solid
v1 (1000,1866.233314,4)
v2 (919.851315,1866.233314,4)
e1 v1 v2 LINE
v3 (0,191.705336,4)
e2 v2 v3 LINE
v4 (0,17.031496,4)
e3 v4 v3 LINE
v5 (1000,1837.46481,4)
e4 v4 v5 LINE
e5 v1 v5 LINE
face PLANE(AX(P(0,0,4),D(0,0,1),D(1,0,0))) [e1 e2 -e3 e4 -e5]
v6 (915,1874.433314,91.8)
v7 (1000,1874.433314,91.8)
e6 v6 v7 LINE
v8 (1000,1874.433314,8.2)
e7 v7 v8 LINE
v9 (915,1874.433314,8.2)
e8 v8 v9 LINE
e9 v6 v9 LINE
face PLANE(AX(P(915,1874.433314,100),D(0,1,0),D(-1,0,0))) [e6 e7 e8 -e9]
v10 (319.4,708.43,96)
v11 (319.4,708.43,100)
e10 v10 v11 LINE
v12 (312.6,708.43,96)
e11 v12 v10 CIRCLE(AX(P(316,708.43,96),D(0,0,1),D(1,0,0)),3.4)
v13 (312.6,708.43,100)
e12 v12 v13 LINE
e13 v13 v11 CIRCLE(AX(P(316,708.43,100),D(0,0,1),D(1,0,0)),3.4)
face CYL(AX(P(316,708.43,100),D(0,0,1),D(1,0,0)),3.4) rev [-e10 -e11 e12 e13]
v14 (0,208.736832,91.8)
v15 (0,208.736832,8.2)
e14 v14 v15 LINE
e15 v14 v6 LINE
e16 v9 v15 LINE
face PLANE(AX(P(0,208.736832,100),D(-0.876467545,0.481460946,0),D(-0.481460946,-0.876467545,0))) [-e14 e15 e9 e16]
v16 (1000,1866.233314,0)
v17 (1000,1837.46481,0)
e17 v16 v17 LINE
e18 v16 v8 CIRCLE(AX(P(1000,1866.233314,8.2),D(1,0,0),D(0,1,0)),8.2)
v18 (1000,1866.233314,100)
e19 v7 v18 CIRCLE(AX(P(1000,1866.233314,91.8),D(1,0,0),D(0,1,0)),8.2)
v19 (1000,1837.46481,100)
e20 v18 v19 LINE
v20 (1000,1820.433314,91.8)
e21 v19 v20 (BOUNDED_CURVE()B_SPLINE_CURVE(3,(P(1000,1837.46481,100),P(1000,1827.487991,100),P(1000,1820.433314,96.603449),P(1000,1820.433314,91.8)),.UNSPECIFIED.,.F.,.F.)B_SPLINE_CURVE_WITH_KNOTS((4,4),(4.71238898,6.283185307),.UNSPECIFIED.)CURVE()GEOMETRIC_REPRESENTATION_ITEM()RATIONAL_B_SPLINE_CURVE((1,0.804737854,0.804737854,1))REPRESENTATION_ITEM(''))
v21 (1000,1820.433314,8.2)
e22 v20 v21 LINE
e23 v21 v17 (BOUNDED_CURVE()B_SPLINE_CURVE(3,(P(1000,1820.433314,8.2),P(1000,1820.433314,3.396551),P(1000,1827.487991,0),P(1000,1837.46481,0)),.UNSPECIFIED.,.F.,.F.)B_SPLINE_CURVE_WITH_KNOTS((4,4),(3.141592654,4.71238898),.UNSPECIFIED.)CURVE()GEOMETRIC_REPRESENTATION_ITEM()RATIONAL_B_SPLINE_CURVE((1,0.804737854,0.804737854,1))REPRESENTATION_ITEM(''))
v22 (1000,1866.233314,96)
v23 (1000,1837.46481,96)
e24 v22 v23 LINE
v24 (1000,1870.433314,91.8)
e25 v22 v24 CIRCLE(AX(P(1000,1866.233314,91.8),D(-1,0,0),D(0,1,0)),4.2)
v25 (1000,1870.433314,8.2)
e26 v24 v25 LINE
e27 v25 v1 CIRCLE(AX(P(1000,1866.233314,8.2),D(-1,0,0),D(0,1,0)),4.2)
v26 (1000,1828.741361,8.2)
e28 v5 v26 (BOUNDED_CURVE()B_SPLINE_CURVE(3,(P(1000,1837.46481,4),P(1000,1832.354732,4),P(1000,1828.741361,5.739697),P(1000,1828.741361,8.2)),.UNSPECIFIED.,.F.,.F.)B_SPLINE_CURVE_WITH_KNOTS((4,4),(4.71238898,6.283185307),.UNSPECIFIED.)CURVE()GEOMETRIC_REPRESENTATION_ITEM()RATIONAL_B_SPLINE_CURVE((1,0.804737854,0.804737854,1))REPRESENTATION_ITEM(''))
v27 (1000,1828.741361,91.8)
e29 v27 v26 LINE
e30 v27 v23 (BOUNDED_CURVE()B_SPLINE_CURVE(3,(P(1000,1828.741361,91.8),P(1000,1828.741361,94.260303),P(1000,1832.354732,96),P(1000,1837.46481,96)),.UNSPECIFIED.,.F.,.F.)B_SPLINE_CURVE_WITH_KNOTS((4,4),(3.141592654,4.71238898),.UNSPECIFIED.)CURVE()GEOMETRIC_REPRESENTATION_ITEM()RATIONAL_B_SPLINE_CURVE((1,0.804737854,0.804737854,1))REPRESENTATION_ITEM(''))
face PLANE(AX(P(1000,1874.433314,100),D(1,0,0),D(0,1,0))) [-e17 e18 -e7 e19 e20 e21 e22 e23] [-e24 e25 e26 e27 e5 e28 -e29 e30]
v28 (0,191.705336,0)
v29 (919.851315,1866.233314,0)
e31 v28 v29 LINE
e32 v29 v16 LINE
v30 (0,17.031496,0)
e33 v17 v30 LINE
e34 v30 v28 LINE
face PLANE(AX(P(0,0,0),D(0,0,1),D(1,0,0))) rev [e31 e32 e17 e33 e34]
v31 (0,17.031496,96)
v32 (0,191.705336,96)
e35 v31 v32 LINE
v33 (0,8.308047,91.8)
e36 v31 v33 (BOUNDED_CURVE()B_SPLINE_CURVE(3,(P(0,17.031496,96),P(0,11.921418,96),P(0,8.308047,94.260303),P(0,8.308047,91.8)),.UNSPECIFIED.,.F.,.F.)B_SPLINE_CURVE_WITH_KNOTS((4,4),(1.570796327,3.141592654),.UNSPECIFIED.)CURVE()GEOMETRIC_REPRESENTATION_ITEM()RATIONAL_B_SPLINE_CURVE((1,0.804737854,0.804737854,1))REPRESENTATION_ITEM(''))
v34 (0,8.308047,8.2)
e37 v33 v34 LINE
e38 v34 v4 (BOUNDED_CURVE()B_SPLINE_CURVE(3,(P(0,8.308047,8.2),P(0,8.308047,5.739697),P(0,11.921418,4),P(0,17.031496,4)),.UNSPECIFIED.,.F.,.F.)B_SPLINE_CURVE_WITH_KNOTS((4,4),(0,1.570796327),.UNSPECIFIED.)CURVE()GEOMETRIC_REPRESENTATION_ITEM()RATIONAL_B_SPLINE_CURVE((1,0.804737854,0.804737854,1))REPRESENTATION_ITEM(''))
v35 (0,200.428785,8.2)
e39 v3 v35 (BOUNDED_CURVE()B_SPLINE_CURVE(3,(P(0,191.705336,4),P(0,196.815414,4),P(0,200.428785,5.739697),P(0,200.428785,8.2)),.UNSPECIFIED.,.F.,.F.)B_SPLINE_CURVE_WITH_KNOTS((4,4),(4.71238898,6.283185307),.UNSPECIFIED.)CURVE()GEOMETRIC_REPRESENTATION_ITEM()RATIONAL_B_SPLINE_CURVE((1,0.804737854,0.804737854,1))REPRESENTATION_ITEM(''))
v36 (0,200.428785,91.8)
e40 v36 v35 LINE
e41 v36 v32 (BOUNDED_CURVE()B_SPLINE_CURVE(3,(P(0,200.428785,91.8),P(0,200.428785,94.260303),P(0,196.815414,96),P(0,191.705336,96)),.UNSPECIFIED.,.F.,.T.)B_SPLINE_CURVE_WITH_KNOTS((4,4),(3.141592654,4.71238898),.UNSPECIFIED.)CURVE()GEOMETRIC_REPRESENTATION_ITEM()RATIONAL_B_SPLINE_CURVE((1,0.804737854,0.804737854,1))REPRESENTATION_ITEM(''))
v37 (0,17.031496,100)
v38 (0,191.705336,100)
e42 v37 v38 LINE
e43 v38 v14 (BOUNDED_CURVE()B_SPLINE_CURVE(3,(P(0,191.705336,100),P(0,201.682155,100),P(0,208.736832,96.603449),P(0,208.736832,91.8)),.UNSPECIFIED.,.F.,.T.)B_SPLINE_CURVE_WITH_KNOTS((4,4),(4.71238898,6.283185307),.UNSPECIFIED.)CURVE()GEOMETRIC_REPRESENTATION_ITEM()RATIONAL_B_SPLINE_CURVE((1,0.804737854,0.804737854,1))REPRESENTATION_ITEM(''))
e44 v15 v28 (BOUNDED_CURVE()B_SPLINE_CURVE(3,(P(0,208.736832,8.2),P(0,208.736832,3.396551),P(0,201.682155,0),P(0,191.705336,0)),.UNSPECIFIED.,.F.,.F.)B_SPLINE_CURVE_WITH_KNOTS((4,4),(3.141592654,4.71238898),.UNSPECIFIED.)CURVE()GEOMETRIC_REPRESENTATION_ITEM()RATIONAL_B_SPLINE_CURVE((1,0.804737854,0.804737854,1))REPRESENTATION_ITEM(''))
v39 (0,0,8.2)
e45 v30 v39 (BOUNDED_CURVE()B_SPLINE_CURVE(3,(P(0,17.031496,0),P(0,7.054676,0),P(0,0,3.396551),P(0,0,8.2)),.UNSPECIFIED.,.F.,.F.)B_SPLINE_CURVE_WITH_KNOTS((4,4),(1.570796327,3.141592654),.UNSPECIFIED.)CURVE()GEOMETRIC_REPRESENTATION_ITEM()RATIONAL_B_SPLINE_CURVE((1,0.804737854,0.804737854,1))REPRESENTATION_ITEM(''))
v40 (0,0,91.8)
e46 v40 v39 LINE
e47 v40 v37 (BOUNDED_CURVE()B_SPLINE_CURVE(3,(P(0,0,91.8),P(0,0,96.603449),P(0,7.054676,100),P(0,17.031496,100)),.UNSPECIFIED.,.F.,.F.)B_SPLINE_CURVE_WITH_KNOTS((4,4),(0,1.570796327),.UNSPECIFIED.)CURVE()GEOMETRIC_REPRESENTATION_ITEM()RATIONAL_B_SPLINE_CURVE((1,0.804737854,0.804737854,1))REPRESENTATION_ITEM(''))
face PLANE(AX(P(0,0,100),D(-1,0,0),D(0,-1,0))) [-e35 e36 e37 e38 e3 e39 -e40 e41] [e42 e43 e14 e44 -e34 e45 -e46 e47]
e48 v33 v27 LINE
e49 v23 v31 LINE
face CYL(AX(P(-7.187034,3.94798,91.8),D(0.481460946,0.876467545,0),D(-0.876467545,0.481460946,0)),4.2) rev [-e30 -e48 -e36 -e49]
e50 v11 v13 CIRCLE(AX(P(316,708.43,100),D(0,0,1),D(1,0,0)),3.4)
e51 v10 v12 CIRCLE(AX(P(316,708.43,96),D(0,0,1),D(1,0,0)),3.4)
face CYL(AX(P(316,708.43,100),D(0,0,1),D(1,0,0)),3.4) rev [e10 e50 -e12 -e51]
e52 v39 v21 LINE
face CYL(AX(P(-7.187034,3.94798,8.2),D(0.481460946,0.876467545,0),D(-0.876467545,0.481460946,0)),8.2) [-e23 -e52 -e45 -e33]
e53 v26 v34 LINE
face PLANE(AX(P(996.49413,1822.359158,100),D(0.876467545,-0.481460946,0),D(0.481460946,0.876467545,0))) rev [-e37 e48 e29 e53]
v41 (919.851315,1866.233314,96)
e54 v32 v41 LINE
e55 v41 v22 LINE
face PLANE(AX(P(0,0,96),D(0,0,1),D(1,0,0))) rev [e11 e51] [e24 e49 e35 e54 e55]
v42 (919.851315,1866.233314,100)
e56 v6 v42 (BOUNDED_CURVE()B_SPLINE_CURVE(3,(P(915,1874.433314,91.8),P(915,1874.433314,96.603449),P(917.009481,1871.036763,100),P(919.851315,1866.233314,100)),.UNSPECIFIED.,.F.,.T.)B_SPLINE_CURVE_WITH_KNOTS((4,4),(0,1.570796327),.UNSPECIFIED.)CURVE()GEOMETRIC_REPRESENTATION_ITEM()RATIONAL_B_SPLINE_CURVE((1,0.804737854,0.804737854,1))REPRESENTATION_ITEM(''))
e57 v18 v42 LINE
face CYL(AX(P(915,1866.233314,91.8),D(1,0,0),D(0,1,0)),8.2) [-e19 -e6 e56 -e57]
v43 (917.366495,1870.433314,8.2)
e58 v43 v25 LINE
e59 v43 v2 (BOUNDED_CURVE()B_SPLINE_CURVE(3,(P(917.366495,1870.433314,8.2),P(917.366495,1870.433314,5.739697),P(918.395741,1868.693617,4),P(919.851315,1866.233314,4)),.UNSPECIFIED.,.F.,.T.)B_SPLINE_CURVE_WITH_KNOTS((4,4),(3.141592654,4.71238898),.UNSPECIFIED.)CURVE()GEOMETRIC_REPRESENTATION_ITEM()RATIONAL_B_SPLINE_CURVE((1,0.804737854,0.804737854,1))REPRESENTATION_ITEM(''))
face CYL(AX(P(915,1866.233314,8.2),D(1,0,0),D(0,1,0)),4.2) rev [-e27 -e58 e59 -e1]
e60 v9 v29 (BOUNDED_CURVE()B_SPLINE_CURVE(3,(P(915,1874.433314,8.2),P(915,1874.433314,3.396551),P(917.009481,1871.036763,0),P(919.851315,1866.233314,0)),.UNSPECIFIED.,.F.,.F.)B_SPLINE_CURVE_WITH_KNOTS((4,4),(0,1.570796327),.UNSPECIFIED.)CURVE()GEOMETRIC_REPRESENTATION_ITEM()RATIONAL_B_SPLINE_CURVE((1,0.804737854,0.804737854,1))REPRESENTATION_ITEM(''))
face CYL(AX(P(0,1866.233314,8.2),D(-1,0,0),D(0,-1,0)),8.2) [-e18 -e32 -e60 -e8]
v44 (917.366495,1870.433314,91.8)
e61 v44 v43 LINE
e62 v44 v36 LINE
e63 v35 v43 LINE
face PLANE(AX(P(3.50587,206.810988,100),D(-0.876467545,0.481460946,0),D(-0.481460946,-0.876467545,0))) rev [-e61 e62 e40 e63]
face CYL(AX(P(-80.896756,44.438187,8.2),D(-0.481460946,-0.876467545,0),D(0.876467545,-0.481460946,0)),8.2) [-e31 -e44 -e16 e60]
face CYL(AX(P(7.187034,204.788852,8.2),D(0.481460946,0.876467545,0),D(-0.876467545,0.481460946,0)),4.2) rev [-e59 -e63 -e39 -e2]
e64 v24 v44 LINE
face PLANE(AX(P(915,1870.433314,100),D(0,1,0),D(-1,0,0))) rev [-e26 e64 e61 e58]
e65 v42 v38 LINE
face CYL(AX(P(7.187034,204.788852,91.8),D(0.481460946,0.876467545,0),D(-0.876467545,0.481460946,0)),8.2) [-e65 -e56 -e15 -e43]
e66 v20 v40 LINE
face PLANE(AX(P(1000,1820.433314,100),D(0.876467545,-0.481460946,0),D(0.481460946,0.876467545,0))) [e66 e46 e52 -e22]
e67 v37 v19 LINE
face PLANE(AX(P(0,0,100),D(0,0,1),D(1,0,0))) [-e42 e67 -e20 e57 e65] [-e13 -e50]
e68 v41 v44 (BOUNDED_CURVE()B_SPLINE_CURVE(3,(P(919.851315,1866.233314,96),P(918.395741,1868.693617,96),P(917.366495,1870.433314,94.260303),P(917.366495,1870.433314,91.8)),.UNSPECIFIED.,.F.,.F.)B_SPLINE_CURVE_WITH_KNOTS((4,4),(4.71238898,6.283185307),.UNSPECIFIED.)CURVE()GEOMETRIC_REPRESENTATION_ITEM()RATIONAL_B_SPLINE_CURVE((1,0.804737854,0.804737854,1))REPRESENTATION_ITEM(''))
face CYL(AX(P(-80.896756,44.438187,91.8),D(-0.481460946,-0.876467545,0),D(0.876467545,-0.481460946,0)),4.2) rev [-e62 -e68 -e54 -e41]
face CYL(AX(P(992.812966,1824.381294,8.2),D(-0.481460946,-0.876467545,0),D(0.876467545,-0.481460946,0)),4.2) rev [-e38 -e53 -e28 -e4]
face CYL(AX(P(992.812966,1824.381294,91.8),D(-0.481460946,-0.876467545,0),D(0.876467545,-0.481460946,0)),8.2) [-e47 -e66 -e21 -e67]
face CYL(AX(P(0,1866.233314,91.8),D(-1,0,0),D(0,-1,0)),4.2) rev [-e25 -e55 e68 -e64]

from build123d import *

# Parameters (mm, degrees)
BOSS_EXTRUDE1_DEPTH   = 100
SHELL1_T              = -4
FILLET1_R             = 8.2
FILLET2_R             = 4.2
M8_TAPPED_HOLE1_D     = 6.8
M8_TAPPED_HOLE1_DEPTH = 19.75
M8_TAPPED_HOLE1_TIP   = 2.042926105


with BuildPart() as part:
    # Sketch1 → Boss-Extrude1 (new body)
    with BuildSketch(Plane.XY):
        Polygon((0, 0), (0, 208.736831721), (915, 1874.433314365), (1000, 1874.433314365), (1000, 1820.433314365), align=None)
    extrude(amount=BOSS_EXTRUDE1_DEPTH)

    # Shell1
    shell1_openings = [part.faces().sort_by_distance(p)[0] for p in [
        (0, 104.36841586, 50),
        (1000, 1847.433314365, 50),
    ]]
    offset(amount=SHELL1_T, openings=shell1_openings, kind=Kind.INTERSECTION)

    # Fillet1
    fillet1_edges = [part.edges().sort_by_distance(p)[0] for p in [
        (457.5, 1041.585073043, 100),
        (957.5, 1874.433314365, 100),
        (957.5, 1874.433314365, 0),
        (457.5, 1041.585073043, 0),
        (500, 910.216657182, 0),
        (500, 910.216657182, 100),
    ]]
    fillet(fillet1_edges, radius=FILLET1_R)

    # Fillet2
    fillet2_edges = [part.edges().sort_by_distance(p)[0] for p in [
        (958.683247588, 1870.433314365, 96),
        (458.683247588, 1035.431049715, 96),
        (500, 918.524703838, 96),
        (500, 918.524703838, 4),
        (458.683247588, 1035.431049715, 4),
        (958.683247588, 1870.433314365, 4),
    ]]
    fillet(fillet2_edges, radius=FILLET2_R)

    # M8 Tapped Hole1
    with Locations(Plane.XY.offset(100)):
        with Locations((316, 708.43)):
            Hole(M8_TAPPED_HOLE1_D / 2, depth=M8_TAPPED_HOLE1_DEPTH)
            with Locations((0, 0, -(M8_TAPPED_HOLE1_DEPTH + M8_TAPPED_HOLE1_TIP / 2))):  # 118° drill point
                Cone(0, M8_TAPPED_HOLE1_D / 2, M8_TAPPED_HOLE1_TIP, mode=Mode.SUBTRACT)


solid = part.part
